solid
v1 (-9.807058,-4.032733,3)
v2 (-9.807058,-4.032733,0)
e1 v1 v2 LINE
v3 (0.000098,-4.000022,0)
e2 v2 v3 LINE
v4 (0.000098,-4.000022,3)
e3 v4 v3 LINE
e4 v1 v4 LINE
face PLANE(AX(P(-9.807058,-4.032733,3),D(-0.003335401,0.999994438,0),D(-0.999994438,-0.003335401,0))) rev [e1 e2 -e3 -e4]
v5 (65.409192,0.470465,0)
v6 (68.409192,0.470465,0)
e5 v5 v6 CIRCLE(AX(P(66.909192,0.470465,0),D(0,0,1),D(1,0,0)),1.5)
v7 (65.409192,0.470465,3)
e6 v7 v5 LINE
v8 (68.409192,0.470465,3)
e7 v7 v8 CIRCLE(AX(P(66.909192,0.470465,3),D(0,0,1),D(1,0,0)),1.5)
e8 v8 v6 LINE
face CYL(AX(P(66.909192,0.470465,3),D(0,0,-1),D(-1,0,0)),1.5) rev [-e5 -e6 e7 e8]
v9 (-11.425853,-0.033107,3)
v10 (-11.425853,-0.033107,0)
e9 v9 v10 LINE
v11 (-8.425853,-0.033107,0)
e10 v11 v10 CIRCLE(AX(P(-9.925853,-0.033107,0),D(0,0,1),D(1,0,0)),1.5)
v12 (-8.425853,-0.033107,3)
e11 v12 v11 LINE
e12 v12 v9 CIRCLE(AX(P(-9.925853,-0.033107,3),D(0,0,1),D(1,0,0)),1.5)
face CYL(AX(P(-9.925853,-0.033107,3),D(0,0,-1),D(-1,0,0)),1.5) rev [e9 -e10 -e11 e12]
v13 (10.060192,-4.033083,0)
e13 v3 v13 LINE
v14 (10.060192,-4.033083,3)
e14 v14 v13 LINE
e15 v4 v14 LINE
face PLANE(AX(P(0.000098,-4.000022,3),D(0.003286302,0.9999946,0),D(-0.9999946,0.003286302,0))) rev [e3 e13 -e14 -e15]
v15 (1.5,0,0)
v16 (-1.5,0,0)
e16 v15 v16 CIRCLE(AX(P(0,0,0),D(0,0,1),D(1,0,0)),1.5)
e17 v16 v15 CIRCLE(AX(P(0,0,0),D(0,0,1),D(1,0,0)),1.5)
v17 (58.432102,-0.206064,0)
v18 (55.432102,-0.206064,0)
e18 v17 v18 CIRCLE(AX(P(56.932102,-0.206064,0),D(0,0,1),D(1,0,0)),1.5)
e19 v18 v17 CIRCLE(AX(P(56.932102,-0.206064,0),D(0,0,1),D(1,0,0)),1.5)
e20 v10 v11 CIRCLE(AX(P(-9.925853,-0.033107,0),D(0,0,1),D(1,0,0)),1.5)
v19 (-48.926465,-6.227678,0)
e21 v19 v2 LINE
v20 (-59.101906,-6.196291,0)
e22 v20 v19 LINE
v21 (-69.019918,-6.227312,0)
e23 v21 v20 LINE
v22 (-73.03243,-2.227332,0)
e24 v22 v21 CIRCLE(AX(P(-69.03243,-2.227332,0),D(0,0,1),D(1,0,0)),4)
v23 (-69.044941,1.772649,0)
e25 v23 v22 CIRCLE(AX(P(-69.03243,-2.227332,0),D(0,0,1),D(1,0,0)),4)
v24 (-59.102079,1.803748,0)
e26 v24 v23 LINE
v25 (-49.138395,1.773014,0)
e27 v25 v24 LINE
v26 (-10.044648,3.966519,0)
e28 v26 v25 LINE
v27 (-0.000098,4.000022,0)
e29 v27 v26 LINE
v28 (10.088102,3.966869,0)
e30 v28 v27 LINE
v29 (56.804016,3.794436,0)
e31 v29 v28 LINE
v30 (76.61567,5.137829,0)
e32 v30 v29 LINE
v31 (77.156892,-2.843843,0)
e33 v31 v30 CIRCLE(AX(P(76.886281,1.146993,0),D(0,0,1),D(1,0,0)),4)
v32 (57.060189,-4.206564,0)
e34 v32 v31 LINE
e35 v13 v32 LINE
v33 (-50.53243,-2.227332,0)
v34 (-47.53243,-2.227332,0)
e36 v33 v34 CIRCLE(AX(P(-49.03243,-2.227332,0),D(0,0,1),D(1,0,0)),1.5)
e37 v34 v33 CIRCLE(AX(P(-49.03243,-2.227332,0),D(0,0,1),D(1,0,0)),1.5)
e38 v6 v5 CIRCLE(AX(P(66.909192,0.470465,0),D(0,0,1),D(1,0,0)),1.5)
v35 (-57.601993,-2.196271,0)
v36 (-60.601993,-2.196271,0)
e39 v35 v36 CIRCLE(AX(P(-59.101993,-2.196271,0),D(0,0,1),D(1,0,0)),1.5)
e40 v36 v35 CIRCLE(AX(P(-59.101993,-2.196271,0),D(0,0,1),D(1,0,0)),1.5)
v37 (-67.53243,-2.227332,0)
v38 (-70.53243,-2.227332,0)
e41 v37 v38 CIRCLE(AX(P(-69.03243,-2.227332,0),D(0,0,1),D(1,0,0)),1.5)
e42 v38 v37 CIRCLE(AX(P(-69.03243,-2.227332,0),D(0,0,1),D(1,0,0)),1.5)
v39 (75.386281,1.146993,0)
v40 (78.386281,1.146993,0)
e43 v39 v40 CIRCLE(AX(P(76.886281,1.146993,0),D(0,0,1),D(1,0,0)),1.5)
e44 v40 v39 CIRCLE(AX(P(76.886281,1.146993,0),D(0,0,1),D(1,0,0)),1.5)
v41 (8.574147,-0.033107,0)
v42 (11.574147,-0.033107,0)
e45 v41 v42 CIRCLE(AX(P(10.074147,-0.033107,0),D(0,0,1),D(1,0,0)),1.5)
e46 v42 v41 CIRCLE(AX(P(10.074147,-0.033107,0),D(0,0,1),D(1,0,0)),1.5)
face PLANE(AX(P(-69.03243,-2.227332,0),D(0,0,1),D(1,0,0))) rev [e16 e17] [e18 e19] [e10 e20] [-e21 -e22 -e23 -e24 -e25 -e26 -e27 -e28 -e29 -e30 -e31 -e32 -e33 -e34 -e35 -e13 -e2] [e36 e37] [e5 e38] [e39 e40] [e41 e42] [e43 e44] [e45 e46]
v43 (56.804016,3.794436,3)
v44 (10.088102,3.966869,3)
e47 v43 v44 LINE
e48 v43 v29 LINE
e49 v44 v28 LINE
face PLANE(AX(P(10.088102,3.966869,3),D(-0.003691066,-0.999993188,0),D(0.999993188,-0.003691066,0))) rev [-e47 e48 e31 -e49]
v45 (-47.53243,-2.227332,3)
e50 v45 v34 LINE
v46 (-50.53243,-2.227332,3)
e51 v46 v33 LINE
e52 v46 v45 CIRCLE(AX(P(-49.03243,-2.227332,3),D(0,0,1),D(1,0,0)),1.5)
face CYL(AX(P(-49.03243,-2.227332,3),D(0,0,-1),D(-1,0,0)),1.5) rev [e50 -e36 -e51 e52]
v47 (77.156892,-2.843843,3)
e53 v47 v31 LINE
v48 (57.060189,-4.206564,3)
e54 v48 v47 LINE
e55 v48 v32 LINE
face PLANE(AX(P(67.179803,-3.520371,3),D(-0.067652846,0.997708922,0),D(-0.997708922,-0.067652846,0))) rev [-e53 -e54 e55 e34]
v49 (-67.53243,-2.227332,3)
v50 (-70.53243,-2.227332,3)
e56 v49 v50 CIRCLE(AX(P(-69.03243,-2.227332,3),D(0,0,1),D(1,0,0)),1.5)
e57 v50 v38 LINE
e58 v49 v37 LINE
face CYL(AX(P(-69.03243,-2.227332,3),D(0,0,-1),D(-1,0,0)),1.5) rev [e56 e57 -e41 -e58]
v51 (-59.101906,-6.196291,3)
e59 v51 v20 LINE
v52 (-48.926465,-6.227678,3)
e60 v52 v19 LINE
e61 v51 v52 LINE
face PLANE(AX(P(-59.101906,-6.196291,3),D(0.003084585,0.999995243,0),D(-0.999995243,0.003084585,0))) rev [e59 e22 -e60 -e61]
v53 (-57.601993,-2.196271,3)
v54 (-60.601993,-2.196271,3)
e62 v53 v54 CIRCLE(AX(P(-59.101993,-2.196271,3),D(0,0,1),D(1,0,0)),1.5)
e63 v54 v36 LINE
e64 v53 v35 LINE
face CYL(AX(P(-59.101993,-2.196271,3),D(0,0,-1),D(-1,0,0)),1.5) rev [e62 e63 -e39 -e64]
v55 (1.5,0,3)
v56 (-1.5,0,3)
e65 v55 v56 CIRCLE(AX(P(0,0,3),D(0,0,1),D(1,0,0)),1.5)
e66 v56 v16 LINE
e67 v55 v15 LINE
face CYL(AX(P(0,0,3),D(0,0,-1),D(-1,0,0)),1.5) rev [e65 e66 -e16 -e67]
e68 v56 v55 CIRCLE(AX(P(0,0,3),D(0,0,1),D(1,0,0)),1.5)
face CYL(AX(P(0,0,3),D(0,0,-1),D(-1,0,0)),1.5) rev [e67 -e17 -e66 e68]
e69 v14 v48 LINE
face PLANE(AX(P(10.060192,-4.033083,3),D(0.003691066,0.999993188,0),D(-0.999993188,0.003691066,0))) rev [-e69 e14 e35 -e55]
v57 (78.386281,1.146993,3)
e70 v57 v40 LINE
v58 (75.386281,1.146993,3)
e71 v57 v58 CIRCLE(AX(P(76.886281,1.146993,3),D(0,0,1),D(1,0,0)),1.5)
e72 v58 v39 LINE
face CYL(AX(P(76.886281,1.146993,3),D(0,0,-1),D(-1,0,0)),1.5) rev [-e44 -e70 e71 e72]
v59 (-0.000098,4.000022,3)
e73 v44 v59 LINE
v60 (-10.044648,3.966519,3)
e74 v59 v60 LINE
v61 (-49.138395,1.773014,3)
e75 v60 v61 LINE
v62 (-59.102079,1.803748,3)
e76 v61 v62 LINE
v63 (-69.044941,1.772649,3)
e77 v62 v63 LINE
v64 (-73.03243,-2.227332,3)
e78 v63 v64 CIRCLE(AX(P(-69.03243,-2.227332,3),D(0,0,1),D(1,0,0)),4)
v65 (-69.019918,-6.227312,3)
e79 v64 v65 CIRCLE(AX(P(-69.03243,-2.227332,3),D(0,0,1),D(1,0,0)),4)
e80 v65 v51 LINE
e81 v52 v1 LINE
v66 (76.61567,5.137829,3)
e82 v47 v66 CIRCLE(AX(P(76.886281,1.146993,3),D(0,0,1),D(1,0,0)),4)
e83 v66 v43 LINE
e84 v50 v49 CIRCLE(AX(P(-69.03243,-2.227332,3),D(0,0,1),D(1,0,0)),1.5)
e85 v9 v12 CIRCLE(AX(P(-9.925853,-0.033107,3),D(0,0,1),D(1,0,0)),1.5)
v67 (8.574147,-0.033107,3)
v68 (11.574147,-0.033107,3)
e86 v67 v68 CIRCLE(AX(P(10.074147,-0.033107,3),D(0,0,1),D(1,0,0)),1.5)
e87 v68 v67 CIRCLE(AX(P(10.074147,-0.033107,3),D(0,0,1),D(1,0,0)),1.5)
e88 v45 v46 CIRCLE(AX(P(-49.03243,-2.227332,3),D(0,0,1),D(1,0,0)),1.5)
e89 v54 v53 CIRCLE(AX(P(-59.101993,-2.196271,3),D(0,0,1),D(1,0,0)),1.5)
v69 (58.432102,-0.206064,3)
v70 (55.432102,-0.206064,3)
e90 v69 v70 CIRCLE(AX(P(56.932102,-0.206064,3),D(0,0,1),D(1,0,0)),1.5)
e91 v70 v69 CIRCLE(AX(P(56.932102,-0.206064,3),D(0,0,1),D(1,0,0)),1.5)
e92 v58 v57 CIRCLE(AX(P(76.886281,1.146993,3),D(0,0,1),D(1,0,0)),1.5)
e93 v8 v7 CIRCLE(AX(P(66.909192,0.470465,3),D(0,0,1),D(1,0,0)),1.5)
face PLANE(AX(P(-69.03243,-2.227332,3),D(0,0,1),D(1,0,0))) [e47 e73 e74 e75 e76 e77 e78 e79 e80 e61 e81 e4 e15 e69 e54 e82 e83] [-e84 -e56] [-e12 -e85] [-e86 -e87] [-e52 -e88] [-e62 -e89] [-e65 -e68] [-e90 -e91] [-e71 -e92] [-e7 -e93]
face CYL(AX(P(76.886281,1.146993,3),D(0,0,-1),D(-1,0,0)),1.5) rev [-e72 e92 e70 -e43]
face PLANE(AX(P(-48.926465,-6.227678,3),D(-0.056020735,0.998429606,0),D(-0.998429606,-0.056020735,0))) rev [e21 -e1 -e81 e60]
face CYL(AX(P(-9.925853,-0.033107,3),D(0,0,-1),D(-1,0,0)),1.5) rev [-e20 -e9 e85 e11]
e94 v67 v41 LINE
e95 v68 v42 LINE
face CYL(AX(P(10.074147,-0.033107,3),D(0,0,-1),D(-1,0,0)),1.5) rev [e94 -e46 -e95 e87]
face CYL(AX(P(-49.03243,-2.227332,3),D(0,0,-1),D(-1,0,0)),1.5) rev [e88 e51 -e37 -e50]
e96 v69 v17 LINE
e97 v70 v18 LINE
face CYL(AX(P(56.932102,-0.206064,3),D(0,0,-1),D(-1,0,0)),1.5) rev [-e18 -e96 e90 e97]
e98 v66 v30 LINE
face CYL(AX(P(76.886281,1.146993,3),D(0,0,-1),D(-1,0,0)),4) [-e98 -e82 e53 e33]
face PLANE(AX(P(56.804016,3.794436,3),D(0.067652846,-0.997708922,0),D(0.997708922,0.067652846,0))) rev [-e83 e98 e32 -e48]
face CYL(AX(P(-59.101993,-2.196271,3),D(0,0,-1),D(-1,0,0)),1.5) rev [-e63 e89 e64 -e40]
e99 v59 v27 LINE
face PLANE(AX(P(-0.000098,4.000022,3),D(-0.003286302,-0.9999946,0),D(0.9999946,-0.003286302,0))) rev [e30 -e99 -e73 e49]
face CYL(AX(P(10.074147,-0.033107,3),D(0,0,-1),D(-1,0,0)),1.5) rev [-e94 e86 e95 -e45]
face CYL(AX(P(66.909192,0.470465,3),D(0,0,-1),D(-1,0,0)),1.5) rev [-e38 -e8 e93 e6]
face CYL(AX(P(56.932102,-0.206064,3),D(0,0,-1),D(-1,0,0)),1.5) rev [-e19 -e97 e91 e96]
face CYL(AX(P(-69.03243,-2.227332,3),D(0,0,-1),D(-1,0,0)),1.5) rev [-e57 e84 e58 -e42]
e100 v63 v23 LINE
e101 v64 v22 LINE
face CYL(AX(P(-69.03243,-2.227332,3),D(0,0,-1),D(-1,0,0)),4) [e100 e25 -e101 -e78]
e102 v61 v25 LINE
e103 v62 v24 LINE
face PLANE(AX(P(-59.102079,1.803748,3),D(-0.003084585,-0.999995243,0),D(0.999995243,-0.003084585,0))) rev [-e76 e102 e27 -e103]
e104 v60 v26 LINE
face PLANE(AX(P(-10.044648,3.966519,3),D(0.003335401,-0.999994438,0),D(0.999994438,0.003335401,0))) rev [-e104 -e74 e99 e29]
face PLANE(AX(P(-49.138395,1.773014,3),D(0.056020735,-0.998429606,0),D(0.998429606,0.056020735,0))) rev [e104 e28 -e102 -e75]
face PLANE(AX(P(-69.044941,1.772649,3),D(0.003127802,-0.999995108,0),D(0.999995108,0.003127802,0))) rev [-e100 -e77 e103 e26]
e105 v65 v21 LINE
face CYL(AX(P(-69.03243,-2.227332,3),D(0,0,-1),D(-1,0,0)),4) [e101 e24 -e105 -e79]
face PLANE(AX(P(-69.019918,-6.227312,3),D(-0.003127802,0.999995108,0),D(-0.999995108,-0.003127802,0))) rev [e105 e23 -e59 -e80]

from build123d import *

# Parameters (mm, degrees)
SKETCH1_R           = 1.5
BOSS_EXTRUDE1_DEPTH = 3


with BuildPart() as part:
    # Sketch1 → Boss-Extrude1 (new body)
    with BuildSketch(Plane.XY):
        with BuildLine():
            Line((-69.019918417, -6.227312299), (-59.101906393, -6.196290568))
            Line((-59.101906393, -6.196290568), (-48.926464715, -6.227677735))
            Line((-48.926464715, -6.227677735), (-9.807058311, -4.032732904))
            Line((-9.807058311, -4.032732904), (9.82e-05, -4.000021922))
            Line((9.82e-05, -4.000021922), (10.060192173, -4.033082606))
            Line((10.060192173, -4.033082606), (57.060189179, -4.206563863))
            Line((57.060189179, -4.206563863), (67.179803064, -3.520371058))
            Line((67.179803064, -3.520371058), (77.15689228, -2.843842595))
            ThreePointArc((77.15689228, -2.843842595), (80.877116582, 1.417604476), (76.61566951, 5.137828778))
            Line((76.61566951, 5.137828778), (66.638580293, 4.461300315))
            Line((66.638580293, 4.461300315), (56.804015745, 3.794436193))
            Line((56.804015745, 3.794436193), (10.088101644, 3.966868874))
            Line((10.088101644, 3.966868874), (-9.82e-05, 4.000021922))
            Line((-9.82e-05, 4.000021922), (-10.044647872, 3.966519135))
            Line((-10.044647872, 3.966519135), (-49.138394535, 1.773014043))
            Line((-49.138394535, 1.773014043), (-59.102079262, 1.803748024))
            Line((-59.102079262, 1.803748024), (-69.044940833, 1.772648568))
            ThreePointArc((-69.044940833, 1.772648568), (-73.032410059, -2.239843074), (-69.019918417, -6.227312299))
        make_face()
        with Locations((-69.032429625, -2.227331865)):
            Circle(SKETCH1_R, mode=Mode.SUBTRACT)
        with Locations((-59.101992828, -2.196271272)):
            Circle(SKETCH1_R, mode=Mode.SUBTRACT)
        with Locations((-49.032429625, -2.227331846)):
            Circle(SKETCH1_R, mode=Mode.SUBTRACT)
        with Locations((-9.925853092, -0.033106885)):
            Circle(SKETCH1_R, mode=Mode.SUBTRACT)
        Circle(SKETCH1_R, mode=Mode.SUBTRACT)
        with Locations((10.074146909, -0.033106866)):
            Circle(SKETCH1_R, mode=Mode.SUBTRACT)
        with Locations((56.932102462, -0.206063835)):
            Circle(SKETCH1_R, mode=Mode.SUBTRACT)
        with Locations((66.909191678, 0.470464628)):
            Circle(SKETCH1_R, mode=Mode.SUBTRACT)
        with Locations((76.886280895, 1.146993091)):
            Circle(SKETCH1_R, mode=Mode.SUBTRACT)
    extrude(amount=BOSS_EXTRUDE1_DEPTH)


solid = part.part
